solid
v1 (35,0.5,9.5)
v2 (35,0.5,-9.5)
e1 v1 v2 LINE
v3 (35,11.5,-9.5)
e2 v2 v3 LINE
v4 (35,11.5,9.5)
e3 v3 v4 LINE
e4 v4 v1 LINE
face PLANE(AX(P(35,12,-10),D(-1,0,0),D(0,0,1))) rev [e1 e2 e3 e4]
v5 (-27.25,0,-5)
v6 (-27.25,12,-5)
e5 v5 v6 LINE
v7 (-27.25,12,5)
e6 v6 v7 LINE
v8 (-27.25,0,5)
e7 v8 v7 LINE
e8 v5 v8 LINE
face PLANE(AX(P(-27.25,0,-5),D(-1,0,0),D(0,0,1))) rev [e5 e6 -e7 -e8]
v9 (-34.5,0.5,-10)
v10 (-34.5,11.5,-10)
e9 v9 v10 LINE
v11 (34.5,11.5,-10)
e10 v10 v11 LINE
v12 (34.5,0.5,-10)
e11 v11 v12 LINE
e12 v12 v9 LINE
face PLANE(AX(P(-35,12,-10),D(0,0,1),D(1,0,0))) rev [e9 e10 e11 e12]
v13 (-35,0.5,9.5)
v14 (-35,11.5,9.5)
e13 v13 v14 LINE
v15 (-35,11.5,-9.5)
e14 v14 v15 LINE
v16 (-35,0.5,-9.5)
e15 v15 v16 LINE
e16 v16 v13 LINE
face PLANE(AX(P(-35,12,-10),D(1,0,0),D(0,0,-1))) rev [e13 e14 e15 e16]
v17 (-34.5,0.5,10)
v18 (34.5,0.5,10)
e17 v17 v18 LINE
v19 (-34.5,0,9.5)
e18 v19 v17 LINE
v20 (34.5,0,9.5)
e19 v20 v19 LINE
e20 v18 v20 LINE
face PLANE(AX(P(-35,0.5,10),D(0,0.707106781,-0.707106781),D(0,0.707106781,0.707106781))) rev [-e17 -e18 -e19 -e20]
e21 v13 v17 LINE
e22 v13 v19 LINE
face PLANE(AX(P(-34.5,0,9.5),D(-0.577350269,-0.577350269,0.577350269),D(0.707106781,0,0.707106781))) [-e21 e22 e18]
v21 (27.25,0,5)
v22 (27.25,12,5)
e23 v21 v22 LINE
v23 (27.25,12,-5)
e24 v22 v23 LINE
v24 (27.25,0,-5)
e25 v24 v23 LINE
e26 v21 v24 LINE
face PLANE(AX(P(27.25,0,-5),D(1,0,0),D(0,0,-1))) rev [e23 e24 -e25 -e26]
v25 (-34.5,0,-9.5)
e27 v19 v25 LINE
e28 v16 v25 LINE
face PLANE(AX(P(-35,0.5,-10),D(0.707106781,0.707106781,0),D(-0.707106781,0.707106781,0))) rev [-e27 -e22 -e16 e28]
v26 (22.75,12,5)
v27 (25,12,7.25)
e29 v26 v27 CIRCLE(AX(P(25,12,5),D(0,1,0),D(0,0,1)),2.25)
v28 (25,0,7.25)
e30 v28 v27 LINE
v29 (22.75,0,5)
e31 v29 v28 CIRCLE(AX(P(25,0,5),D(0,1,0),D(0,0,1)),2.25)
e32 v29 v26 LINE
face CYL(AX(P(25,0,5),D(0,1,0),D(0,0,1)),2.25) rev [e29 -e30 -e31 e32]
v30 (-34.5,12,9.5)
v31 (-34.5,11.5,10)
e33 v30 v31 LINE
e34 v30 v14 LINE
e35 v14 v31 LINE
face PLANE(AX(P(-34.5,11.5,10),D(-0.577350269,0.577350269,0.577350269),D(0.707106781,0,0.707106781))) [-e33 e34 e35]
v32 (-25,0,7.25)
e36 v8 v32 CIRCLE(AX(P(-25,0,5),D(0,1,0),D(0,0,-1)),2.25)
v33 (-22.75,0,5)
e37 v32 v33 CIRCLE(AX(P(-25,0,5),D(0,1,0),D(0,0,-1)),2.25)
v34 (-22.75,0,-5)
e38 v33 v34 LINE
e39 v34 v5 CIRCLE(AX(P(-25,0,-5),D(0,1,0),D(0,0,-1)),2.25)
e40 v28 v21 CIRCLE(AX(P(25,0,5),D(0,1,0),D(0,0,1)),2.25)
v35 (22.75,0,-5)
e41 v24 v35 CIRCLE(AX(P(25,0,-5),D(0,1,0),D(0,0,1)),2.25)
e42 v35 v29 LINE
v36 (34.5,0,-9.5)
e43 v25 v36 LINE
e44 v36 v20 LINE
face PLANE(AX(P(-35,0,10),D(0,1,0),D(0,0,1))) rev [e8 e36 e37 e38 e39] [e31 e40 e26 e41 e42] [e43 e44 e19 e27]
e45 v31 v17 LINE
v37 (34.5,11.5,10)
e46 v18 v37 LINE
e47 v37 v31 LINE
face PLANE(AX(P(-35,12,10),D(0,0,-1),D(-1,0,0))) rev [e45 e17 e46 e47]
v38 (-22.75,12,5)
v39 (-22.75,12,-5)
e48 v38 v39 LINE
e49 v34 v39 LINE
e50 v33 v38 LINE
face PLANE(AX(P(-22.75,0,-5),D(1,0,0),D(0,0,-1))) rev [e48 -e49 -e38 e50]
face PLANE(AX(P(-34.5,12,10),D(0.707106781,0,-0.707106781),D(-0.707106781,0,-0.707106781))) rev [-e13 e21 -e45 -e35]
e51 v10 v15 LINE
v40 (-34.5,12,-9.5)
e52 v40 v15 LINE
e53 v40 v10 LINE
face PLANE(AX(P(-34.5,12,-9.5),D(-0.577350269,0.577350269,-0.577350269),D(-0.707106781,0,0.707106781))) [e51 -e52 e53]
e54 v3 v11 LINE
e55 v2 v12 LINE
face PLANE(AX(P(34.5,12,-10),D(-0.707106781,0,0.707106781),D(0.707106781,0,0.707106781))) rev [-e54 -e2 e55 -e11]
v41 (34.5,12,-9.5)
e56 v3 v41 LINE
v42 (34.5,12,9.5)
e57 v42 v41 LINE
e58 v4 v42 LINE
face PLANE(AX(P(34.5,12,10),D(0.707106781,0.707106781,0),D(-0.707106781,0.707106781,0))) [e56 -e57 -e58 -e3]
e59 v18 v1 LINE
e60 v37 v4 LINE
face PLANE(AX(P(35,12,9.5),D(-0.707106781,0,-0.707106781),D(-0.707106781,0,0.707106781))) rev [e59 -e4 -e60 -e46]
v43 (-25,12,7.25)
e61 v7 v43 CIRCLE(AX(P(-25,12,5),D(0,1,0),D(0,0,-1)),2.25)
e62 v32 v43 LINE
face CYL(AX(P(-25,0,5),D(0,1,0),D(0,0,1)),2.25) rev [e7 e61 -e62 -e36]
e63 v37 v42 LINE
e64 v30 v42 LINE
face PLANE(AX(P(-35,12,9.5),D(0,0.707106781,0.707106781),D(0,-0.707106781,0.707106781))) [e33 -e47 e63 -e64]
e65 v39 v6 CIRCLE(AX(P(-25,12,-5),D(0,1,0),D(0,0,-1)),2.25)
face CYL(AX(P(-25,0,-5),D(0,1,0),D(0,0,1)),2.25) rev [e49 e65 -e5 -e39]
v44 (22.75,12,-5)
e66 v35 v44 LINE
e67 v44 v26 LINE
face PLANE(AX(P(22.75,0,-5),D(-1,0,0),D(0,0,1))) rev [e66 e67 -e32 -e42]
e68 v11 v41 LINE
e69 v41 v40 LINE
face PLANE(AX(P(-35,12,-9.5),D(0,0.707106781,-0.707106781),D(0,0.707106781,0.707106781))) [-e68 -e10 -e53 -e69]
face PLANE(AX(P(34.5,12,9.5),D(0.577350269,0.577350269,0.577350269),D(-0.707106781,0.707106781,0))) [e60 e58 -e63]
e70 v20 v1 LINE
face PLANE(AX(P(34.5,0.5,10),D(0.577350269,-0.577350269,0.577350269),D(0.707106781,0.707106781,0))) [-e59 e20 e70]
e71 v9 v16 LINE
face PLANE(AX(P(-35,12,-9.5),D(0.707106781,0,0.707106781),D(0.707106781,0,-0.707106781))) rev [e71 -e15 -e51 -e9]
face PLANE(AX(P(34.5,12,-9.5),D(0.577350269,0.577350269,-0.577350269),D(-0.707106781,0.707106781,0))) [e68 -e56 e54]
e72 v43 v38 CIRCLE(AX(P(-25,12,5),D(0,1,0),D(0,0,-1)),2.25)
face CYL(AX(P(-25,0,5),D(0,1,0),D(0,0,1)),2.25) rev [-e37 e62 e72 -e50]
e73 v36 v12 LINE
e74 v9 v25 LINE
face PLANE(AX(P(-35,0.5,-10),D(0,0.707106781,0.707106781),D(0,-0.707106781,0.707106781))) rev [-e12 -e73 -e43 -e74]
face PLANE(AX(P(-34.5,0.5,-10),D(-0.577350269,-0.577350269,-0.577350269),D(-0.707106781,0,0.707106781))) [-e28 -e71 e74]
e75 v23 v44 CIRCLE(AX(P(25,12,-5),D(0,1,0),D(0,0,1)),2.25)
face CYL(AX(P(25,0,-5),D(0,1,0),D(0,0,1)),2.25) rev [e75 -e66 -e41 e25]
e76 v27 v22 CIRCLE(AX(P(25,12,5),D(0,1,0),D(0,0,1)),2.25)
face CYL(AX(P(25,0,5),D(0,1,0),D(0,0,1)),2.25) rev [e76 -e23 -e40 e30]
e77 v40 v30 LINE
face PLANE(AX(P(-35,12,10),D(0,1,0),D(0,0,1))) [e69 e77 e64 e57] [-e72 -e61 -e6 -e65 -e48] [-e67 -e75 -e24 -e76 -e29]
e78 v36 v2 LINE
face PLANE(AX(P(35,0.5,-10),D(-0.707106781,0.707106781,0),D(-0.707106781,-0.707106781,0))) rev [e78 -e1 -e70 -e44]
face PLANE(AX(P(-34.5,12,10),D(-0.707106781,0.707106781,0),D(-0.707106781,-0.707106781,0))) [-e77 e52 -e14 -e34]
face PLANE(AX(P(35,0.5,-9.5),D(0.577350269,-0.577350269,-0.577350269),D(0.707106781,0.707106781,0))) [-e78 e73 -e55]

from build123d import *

# Parameters (mm, degrees)
SKETCH1_W          = 70
SKETCH1_H          = 20
EXTRUDE1_DEPTH     = 12
CUT_EXTRUDE1_DEPTH = 39.327535793
CHAMFER1_SIZE      = 0.5


with BuildPart() as part:
    # Sketch1 → Extrude1 (new body)
    with BuildSketch(Plane(origin=(0, 0, 0), x_dir=(1, 0, 0), z_dir=(0, 1, 0))):
        Rectangle(SKETCH1_W, SKETCH1_H)
    extrude(amount=EXTRUDE1_DEPTH)

    # Sketch2 → Cut-Extrude1 (cut, through all)
    with BuildSketch(Plane(origin=(0, 12, 0), x_dir=(1, 0, 0), z_dir=(0, 1, 0))):
        with BuildLine():
            Line((22.75, 5), (22.75, -5))
            ThreePointArc((22.75, -5), (25, -7.25), (27.25, -5))
            Line((27.25, -5), (27.25, 5))
            ThreePointArc((27.25, 5), (25, 7.25), (22.75, 5))
        make_face()
        with BuildLine():
            Line((-27.25, 5), (-27.25, -5))
            ThreePointArc((-27.25, -5), (-25, -7.25), (-22.75, -5))
            Line((-22.75, -5), (-22.75, 5))
            ThreePointArc((-22.75, 5), (-25, 7.25), (-27.25, 5))
        make_face()
    extrude(amount=-CUT_EXTRUDE1_DEPTH, mode=Mode.SUBTRACT)

    # Chamfer1
    chamfer1_edges = [part.edges().sort_by_distance(p)[0] for p in [
        (35, 12, 0),
        (0, 12, -10),
        (-35, 12, 0),
        (0, 0, -10),
        (35, 0, 0),
        (0, 0, 10),
        (-35, 0, 0),
        (0, 12, 10),
        (-35, 6, -10),
        (35, 6, -10),
        (35, 6, 10),
        (-35, 6, 10),
    ]]
    chamfer(chamfer1_edges, length=CHAMFER1_SIZE)


solid = part.part
